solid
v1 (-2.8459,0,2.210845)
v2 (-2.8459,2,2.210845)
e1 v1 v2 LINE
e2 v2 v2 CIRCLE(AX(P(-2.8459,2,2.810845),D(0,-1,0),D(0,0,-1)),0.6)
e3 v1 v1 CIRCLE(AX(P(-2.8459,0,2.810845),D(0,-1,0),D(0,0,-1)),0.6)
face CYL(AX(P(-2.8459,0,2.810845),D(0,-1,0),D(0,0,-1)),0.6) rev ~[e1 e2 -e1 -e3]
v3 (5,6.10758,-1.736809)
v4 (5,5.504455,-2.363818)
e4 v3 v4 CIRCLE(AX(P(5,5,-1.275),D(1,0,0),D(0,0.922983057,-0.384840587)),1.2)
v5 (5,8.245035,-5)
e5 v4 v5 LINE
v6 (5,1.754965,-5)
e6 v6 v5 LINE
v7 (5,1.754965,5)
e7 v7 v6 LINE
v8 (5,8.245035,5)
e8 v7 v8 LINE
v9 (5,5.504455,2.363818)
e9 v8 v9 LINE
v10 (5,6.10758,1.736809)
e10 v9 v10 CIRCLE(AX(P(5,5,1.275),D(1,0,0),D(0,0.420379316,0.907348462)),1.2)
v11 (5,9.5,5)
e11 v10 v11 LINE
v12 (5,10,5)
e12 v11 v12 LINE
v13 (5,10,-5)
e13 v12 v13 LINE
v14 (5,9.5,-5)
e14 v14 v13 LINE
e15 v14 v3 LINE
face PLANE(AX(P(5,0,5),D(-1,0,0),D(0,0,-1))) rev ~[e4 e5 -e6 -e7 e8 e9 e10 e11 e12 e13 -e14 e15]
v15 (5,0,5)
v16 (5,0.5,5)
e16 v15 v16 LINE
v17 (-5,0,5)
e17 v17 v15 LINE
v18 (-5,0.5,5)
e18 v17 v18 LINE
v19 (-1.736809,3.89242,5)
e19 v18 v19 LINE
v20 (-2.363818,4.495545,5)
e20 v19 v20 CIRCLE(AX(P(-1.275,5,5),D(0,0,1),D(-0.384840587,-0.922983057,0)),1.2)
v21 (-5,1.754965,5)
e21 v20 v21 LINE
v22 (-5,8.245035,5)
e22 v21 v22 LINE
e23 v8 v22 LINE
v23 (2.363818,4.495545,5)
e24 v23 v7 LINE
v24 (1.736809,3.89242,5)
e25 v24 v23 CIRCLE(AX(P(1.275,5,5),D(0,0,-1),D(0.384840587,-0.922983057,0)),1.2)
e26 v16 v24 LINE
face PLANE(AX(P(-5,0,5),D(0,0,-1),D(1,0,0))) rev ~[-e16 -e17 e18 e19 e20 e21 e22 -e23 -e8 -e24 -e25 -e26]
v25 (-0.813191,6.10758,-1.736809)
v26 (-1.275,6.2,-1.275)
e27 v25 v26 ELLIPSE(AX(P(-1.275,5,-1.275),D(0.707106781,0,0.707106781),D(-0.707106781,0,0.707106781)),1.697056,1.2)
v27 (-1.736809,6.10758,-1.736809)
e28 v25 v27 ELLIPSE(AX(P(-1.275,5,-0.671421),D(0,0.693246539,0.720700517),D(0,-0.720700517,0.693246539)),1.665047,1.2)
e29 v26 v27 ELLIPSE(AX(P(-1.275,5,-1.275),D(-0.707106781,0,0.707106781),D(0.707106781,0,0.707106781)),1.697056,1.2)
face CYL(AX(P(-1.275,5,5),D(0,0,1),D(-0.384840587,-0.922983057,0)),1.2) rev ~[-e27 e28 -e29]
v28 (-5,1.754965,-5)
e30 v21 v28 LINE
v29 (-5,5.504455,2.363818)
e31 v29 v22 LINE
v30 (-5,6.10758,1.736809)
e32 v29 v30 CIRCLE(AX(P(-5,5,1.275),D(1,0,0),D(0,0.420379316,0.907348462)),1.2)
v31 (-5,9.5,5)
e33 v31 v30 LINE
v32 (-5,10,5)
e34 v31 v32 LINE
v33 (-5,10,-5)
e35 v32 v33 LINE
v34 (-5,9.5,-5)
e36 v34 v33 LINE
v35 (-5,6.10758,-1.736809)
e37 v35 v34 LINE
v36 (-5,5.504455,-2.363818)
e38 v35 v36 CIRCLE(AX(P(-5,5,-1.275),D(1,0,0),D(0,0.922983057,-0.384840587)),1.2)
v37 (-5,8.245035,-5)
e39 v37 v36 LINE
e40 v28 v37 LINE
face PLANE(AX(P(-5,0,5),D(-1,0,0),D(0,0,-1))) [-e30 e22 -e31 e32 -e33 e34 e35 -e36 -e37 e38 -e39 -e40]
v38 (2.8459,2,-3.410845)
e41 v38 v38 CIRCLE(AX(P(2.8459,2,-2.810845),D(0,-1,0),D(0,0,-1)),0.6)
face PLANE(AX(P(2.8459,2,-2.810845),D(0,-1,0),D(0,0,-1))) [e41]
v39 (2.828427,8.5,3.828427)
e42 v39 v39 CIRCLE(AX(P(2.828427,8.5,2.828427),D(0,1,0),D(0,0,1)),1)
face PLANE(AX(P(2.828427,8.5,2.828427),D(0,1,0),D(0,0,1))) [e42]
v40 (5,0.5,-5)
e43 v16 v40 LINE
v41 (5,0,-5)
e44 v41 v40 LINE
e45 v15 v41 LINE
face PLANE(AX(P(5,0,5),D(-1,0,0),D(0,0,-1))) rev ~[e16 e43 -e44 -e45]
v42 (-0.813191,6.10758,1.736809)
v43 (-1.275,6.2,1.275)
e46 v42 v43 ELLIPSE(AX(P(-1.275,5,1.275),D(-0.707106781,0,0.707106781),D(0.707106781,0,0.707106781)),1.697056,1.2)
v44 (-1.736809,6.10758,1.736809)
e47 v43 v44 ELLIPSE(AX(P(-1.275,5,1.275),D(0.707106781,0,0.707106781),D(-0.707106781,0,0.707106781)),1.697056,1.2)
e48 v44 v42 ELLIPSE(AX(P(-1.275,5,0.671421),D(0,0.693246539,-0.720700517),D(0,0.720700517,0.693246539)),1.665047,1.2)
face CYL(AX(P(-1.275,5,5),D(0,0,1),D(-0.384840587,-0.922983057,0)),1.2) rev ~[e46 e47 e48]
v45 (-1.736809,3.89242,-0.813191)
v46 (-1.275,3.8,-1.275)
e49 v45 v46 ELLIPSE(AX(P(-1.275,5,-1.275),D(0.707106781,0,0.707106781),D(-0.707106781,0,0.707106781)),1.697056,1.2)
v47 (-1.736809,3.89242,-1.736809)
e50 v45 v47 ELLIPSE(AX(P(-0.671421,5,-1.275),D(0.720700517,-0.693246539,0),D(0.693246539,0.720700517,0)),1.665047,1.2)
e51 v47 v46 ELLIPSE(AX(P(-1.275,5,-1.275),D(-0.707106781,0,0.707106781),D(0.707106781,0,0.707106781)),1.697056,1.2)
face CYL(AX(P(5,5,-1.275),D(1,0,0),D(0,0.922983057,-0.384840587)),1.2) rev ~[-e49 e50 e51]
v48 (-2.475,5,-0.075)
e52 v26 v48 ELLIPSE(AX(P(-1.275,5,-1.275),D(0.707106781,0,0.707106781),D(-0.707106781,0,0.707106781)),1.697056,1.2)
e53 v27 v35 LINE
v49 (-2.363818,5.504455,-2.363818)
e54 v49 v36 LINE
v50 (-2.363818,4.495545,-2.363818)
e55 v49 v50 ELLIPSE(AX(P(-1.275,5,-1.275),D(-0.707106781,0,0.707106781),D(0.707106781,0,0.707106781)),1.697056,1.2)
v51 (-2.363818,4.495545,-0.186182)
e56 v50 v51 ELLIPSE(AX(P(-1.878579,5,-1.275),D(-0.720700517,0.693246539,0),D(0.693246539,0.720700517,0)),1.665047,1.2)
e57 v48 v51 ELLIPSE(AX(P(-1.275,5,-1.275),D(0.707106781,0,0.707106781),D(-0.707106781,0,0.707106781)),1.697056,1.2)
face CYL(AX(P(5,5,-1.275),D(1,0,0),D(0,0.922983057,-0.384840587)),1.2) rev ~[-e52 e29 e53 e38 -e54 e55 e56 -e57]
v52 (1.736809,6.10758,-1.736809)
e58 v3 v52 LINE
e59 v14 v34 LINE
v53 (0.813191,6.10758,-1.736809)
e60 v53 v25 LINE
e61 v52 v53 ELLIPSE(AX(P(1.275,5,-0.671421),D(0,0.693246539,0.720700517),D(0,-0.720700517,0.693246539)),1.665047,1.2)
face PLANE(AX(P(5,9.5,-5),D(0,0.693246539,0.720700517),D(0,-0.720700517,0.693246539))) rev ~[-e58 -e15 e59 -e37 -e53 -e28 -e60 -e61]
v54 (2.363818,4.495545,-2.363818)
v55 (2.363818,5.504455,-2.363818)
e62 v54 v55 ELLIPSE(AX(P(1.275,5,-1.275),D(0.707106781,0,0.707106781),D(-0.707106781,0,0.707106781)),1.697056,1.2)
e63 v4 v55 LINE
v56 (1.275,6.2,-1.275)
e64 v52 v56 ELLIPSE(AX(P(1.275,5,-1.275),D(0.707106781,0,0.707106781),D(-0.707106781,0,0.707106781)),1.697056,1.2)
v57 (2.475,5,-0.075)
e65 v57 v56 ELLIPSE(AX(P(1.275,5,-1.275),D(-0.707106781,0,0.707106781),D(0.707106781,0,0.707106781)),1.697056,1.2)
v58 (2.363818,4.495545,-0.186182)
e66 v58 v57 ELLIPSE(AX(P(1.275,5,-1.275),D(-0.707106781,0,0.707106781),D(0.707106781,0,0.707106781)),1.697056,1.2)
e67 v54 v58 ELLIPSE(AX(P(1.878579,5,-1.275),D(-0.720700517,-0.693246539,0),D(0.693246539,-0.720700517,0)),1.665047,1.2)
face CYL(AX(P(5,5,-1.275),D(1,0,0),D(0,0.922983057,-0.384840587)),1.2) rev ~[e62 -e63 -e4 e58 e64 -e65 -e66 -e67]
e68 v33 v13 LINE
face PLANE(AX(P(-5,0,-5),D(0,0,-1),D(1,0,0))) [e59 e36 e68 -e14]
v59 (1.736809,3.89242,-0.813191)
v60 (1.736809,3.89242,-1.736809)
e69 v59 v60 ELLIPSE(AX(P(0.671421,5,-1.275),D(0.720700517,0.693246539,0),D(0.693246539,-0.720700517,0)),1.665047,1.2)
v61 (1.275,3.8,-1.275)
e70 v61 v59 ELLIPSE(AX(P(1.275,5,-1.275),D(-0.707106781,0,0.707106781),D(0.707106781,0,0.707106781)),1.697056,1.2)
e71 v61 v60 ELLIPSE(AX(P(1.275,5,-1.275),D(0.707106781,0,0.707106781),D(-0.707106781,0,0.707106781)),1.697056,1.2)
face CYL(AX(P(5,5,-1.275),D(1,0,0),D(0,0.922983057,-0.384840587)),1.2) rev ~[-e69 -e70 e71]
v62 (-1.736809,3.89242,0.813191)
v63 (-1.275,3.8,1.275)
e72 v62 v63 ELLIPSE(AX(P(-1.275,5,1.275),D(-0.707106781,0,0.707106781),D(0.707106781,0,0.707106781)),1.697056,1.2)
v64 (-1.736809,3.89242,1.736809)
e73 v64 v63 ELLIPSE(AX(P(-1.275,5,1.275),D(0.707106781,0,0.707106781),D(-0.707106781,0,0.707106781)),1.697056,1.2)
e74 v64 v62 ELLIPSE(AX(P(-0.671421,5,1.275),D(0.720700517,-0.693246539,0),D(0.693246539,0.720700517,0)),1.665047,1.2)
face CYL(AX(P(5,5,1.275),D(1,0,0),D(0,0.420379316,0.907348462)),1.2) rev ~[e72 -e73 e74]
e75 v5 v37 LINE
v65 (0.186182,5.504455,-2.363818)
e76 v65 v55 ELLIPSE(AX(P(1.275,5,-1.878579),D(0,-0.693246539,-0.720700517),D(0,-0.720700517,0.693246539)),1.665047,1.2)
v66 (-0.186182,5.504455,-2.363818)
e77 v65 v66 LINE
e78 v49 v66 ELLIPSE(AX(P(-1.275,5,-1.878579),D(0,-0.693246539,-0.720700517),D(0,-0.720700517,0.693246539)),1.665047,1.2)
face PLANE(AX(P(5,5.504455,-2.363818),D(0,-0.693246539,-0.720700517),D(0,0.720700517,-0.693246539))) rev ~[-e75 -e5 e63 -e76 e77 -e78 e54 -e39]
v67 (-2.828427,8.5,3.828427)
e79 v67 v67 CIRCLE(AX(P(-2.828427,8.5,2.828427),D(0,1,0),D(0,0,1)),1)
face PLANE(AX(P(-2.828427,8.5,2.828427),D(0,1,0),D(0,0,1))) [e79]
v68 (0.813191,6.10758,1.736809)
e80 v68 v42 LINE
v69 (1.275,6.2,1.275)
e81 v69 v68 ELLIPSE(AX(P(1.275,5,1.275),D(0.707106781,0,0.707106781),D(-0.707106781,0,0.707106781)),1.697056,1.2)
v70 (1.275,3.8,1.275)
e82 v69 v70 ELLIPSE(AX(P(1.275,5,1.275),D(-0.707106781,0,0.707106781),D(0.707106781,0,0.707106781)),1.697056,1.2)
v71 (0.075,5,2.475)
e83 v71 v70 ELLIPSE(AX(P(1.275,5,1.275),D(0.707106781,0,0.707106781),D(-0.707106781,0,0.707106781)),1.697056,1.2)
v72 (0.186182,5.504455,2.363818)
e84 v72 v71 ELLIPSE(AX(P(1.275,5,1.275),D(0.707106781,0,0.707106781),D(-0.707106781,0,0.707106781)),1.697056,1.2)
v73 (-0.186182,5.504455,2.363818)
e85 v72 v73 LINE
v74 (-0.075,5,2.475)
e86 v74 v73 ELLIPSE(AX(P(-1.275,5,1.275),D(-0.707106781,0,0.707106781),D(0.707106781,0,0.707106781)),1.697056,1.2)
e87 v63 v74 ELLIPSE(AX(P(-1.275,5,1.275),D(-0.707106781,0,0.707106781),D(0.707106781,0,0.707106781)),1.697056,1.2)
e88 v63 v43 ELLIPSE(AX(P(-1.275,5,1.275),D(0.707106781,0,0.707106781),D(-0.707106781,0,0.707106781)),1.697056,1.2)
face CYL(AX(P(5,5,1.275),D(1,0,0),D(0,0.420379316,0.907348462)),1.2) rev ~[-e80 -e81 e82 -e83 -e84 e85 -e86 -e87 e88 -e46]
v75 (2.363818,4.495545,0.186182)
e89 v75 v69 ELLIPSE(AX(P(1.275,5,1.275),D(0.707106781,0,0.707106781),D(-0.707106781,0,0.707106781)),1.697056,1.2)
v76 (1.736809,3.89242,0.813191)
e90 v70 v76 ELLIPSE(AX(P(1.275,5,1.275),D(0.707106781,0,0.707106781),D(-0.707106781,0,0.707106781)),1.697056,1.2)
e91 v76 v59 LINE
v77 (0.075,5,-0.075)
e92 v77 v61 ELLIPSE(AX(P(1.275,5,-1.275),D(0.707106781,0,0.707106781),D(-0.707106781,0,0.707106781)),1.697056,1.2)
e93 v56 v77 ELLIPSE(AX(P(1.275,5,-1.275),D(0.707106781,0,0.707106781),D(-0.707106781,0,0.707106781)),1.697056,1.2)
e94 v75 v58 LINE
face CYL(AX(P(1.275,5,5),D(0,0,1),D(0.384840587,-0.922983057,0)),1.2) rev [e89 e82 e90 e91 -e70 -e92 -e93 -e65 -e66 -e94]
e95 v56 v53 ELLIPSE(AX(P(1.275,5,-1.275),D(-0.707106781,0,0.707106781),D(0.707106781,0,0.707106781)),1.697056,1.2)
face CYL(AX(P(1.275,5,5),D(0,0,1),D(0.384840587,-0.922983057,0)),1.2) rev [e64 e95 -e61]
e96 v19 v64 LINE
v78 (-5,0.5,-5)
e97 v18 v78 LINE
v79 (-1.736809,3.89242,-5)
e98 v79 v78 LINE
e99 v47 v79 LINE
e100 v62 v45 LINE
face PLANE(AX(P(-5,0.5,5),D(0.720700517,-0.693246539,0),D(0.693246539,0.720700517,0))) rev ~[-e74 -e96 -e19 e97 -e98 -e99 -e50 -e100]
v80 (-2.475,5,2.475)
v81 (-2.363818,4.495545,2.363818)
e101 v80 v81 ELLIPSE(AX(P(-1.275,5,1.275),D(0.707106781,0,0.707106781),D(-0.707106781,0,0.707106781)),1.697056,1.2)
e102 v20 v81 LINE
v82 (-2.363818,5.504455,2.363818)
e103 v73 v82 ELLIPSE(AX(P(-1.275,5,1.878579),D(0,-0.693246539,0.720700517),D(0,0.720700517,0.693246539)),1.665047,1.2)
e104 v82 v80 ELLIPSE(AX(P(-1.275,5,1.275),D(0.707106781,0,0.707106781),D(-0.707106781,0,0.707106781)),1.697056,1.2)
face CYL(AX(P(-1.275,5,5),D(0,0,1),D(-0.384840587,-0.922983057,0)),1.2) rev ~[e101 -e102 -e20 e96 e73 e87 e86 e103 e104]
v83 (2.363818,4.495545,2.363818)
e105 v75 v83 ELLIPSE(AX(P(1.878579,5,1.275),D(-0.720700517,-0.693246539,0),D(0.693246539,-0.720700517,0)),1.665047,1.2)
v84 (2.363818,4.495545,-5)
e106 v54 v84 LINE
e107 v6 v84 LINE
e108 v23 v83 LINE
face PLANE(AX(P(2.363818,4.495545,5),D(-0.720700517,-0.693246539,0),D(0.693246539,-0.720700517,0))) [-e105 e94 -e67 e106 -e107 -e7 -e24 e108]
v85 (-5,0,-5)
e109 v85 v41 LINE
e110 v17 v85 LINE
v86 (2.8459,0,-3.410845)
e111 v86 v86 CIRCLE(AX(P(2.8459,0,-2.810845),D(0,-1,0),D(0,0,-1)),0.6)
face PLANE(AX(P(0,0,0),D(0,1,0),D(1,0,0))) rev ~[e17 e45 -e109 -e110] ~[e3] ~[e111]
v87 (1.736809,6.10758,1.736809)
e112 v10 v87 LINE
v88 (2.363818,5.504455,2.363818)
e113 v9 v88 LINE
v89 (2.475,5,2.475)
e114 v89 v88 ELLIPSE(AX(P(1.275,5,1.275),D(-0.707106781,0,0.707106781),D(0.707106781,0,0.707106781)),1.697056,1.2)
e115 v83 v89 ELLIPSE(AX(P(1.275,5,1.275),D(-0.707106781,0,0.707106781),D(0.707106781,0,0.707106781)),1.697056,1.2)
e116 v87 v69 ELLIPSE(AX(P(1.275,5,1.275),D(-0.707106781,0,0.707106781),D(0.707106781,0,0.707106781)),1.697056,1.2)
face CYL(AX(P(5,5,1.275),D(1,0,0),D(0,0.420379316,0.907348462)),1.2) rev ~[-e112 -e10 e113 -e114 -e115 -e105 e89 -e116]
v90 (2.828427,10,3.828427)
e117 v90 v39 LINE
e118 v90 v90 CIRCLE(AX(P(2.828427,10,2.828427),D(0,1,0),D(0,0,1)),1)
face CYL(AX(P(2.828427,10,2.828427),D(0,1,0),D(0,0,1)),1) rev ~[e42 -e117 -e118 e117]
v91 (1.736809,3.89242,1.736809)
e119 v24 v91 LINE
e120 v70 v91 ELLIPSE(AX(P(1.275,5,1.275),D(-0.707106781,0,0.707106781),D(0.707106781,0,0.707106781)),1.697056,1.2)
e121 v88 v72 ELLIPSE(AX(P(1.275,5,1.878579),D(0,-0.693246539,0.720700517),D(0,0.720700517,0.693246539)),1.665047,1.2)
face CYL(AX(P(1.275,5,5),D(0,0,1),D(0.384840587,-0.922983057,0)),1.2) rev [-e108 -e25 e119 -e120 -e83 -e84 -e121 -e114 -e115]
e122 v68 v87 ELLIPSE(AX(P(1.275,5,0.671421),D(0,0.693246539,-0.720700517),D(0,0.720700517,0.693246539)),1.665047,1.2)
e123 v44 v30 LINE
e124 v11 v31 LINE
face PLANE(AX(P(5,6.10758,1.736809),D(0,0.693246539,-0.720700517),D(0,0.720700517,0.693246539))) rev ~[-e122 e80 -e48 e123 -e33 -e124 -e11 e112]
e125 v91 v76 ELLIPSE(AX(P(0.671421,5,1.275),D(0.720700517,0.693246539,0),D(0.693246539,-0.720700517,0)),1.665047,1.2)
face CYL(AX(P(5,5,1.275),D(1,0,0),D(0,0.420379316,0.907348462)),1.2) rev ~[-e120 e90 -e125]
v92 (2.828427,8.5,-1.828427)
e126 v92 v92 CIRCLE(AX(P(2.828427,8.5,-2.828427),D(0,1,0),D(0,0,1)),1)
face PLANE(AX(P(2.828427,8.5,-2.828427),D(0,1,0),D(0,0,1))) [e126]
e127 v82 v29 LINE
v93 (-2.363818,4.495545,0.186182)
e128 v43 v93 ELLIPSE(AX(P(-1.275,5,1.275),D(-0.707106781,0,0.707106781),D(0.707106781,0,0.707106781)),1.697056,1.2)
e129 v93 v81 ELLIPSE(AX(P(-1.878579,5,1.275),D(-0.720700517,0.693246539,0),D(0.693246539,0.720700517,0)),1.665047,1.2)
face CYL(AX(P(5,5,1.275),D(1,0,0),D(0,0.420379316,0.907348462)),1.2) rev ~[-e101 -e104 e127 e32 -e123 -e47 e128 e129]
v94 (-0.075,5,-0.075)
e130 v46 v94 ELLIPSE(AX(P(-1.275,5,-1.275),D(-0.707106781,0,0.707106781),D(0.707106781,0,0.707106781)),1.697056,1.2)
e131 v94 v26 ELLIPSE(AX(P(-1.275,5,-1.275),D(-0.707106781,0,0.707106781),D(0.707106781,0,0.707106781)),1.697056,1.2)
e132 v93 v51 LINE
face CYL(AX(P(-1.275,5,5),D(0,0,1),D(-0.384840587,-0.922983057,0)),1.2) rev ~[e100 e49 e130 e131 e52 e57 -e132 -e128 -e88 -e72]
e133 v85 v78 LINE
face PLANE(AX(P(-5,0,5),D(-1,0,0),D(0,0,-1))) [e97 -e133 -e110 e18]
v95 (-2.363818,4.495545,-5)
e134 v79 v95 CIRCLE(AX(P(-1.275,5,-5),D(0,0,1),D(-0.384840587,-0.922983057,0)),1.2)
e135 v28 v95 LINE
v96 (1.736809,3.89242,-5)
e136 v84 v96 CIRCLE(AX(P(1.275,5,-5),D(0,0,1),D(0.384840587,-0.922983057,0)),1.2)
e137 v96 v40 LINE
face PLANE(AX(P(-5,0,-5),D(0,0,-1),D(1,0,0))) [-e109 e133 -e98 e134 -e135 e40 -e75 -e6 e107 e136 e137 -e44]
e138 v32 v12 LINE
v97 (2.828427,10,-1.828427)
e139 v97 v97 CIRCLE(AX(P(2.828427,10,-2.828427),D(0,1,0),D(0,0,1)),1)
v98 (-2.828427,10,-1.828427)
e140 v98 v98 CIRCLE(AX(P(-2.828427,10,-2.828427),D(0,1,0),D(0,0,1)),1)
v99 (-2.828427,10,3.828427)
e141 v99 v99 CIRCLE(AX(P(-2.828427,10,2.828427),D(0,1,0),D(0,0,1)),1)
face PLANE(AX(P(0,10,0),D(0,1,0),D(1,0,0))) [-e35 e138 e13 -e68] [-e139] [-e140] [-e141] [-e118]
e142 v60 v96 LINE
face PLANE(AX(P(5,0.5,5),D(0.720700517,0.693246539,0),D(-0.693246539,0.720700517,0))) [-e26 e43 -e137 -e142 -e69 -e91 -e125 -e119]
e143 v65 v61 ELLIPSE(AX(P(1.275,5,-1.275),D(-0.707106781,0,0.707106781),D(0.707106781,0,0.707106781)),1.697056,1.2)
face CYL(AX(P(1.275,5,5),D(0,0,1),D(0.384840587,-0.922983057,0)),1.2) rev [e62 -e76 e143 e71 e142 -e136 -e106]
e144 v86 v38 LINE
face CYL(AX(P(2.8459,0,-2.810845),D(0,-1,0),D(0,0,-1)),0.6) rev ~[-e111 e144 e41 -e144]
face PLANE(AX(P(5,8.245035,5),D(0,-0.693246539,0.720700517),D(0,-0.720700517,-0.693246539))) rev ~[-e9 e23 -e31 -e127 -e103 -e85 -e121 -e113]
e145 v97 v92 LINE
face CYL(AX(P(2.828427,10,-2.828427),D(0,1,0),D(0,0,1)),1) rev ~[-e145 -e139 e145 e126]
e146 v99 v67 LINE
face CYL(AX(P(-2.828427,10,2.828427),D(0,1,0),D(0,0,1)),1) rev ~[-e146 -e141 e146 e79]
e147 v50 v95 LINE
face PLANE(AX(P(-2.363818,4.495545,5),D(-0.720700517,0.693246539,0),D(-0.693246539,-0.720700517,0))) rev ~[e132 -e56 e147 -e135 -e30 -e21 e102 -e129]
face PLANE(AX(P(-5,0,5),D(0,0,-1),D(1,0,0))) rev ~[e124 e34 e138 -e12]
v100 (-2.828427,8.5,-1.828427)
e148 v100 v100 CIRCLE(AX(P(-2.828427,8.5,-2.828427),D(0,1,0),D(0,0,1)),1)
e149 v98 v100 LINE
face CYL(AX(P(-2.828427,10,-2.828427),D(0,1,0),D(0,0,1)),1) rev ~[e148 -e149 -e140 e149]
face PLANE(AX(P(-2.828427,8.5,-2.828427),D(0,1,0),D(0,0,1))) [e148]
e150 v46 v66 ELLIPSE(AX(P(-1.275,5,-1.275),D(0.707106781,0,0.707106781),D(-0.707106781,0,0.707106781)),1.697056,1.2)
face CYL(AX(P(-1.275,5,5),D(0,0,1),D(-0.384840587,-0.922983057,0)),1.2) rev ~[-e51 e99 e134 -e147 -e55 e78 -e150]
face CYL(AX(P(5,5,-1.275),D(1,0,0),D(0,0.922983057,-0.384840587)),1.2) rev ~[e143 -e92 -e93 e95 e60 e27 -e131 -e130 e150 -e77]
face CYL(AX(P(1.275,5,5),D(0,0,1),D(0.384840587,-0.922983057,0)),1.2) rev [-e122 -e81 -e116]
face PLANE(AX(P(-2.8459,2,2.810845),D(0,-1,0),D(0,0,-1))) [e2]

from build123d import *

# Parameters (mm, degrees)
SKETCH1_W           = 10
SKETCH1_H           = 10
BOSS_EXTRUDE1_DEPTH = 10
CUT_EXTRUDE1_DEPTH  = 16
CUT_EXTRUDE2_DEPTH  = 16
SKETCH5_R           = 0.6
CUT_EXTRUDE3_DEPTH  = 2
SKETCH6_R           = 1
CUT_EXTRUDE4_DEPTH  = 1.5


with BuildPart() as part:
    # Sketch1 → Boss-Extrude1 (new body)
    with BuildSketch(Plane(origin=(0, 0, 0), x_dir=(1, 0, 0), z_dir=(0, 1, 0))):
        Rectangle(SKETCH1_W, SKETCH1_H)
    extrude(amount=BOSS_EXTRUDE1_DEPTH)

    # Sketch2 → Cut-Extrude1 (cut, through all)
    with BuildSketch(Plane.XY.offset(5)):
        with BuildLine():
            Line((2.363818154, 4.495544821), (5, 1.754964793))
            Line((5, 1.754964793), (5, 0.5))
            Line((5, 0.5), (1.736808704, 3.892420332))
            ThreePointArc((1.736808704, 3.892420332), (0.443104153, 5.864840621), (2.363818154, 4.495544821))
        make_face()
        with BuildLine():
            Line((-5, 1.754964793), (-5, 0.5))
            Line((-5, 0.5), (-1.736808704, 3.892420332))
            ThreePointArc((-1.736808704, 3.892420332), (-0.443104153, 5.864840621), (-2.363818154, 4.495544821))
            Line((-2.363818154, 4.495544821), (-5, 1.754964793))
        make_face()
    extrude(amount=-CUT_EXTRUDE1_DEPTH, mode=Mode.SUBTRACT)

    # Sketch3 → Cut-Extrude2 (cut, through all)
    with BuildSketch(Plane(origin=(5, 0, 0), x_dir=(0, 0, -1), z_dir=(1, 0, 0))):
        with BuildLine():
            Line((2.363818154, 5.504455179), (5, 8.245035207))
            Line((5, 8.245035207), (5, 9.5))
            Line((5, 9.5), (1.736808704, 6.107579668))
            ThreePointArc((1.736808704, 6.107579668), (0.443104153, 4.135159379), (2.363818154, 5.504455179))
        make_face()
        with BuildLine():
            Line((-5, 9.5), (-5, 8.245035207))
            Line((-5, 8.245035207), (-2.363818154, 5.504455179))
            ThreePointArc((-2.363818154, 5.504455179), (-0.443104153, 4.135159379), (-1.736808704, 6.107579668))
            Line((-1.736808704, 6.107579668), (-5, 9.5))
        make_face()
    extrude(amount=-CUT_EXTRUDE2_DEPTH, mode=Mode.SUBTRACT)

    # Sketch5 → Cut-Extrude3 (cut)
    with BuildSketch(Plane.XZ):
        with Locations(Location((-2.84590029, 2.810845343, 0), (0, 0, 270))):
            Circle(SKETCH5_R)
        with Locations(Location((2.84590029, -2.810845343, 0), (0, 0, 270))):
            Circle(SKETCH5_R)
    extrude(amount=-CUT_EXTRUDE3_DEPTH, mode=Mode.SUBTRACT)

    # Sketch6 → Cut-Extrude4 (cut)
    with BuildSketch(Plane(origin=(0, 10, 0), x_dir=(1, 0, 0), z_dir=(0, 1, 0))):
        with Locations(Location((-2.828427125, 2.828427125, 0), (0, 0, 270))):
            Circle(SKETCH6_R)
        with Locations(Location((2.828427125, 2.828427125, 0), (0, 0, 270))):
            Circle(SKETCH6_R)
        with Locations(Location((2.828427125, -2.828427125, 0), (0, 0, 270))):
            Circle(SKETCH6_R)
        with Locations(Location((-2.828427125, -2.828427125, 0), (0, 0, 270))):
            Circle(SKETCH6_R)
    extrude(amount=-CUT_EXTRUDE4_DEPTH, mode=Mode.SUBTRACT)


solid = part.part
